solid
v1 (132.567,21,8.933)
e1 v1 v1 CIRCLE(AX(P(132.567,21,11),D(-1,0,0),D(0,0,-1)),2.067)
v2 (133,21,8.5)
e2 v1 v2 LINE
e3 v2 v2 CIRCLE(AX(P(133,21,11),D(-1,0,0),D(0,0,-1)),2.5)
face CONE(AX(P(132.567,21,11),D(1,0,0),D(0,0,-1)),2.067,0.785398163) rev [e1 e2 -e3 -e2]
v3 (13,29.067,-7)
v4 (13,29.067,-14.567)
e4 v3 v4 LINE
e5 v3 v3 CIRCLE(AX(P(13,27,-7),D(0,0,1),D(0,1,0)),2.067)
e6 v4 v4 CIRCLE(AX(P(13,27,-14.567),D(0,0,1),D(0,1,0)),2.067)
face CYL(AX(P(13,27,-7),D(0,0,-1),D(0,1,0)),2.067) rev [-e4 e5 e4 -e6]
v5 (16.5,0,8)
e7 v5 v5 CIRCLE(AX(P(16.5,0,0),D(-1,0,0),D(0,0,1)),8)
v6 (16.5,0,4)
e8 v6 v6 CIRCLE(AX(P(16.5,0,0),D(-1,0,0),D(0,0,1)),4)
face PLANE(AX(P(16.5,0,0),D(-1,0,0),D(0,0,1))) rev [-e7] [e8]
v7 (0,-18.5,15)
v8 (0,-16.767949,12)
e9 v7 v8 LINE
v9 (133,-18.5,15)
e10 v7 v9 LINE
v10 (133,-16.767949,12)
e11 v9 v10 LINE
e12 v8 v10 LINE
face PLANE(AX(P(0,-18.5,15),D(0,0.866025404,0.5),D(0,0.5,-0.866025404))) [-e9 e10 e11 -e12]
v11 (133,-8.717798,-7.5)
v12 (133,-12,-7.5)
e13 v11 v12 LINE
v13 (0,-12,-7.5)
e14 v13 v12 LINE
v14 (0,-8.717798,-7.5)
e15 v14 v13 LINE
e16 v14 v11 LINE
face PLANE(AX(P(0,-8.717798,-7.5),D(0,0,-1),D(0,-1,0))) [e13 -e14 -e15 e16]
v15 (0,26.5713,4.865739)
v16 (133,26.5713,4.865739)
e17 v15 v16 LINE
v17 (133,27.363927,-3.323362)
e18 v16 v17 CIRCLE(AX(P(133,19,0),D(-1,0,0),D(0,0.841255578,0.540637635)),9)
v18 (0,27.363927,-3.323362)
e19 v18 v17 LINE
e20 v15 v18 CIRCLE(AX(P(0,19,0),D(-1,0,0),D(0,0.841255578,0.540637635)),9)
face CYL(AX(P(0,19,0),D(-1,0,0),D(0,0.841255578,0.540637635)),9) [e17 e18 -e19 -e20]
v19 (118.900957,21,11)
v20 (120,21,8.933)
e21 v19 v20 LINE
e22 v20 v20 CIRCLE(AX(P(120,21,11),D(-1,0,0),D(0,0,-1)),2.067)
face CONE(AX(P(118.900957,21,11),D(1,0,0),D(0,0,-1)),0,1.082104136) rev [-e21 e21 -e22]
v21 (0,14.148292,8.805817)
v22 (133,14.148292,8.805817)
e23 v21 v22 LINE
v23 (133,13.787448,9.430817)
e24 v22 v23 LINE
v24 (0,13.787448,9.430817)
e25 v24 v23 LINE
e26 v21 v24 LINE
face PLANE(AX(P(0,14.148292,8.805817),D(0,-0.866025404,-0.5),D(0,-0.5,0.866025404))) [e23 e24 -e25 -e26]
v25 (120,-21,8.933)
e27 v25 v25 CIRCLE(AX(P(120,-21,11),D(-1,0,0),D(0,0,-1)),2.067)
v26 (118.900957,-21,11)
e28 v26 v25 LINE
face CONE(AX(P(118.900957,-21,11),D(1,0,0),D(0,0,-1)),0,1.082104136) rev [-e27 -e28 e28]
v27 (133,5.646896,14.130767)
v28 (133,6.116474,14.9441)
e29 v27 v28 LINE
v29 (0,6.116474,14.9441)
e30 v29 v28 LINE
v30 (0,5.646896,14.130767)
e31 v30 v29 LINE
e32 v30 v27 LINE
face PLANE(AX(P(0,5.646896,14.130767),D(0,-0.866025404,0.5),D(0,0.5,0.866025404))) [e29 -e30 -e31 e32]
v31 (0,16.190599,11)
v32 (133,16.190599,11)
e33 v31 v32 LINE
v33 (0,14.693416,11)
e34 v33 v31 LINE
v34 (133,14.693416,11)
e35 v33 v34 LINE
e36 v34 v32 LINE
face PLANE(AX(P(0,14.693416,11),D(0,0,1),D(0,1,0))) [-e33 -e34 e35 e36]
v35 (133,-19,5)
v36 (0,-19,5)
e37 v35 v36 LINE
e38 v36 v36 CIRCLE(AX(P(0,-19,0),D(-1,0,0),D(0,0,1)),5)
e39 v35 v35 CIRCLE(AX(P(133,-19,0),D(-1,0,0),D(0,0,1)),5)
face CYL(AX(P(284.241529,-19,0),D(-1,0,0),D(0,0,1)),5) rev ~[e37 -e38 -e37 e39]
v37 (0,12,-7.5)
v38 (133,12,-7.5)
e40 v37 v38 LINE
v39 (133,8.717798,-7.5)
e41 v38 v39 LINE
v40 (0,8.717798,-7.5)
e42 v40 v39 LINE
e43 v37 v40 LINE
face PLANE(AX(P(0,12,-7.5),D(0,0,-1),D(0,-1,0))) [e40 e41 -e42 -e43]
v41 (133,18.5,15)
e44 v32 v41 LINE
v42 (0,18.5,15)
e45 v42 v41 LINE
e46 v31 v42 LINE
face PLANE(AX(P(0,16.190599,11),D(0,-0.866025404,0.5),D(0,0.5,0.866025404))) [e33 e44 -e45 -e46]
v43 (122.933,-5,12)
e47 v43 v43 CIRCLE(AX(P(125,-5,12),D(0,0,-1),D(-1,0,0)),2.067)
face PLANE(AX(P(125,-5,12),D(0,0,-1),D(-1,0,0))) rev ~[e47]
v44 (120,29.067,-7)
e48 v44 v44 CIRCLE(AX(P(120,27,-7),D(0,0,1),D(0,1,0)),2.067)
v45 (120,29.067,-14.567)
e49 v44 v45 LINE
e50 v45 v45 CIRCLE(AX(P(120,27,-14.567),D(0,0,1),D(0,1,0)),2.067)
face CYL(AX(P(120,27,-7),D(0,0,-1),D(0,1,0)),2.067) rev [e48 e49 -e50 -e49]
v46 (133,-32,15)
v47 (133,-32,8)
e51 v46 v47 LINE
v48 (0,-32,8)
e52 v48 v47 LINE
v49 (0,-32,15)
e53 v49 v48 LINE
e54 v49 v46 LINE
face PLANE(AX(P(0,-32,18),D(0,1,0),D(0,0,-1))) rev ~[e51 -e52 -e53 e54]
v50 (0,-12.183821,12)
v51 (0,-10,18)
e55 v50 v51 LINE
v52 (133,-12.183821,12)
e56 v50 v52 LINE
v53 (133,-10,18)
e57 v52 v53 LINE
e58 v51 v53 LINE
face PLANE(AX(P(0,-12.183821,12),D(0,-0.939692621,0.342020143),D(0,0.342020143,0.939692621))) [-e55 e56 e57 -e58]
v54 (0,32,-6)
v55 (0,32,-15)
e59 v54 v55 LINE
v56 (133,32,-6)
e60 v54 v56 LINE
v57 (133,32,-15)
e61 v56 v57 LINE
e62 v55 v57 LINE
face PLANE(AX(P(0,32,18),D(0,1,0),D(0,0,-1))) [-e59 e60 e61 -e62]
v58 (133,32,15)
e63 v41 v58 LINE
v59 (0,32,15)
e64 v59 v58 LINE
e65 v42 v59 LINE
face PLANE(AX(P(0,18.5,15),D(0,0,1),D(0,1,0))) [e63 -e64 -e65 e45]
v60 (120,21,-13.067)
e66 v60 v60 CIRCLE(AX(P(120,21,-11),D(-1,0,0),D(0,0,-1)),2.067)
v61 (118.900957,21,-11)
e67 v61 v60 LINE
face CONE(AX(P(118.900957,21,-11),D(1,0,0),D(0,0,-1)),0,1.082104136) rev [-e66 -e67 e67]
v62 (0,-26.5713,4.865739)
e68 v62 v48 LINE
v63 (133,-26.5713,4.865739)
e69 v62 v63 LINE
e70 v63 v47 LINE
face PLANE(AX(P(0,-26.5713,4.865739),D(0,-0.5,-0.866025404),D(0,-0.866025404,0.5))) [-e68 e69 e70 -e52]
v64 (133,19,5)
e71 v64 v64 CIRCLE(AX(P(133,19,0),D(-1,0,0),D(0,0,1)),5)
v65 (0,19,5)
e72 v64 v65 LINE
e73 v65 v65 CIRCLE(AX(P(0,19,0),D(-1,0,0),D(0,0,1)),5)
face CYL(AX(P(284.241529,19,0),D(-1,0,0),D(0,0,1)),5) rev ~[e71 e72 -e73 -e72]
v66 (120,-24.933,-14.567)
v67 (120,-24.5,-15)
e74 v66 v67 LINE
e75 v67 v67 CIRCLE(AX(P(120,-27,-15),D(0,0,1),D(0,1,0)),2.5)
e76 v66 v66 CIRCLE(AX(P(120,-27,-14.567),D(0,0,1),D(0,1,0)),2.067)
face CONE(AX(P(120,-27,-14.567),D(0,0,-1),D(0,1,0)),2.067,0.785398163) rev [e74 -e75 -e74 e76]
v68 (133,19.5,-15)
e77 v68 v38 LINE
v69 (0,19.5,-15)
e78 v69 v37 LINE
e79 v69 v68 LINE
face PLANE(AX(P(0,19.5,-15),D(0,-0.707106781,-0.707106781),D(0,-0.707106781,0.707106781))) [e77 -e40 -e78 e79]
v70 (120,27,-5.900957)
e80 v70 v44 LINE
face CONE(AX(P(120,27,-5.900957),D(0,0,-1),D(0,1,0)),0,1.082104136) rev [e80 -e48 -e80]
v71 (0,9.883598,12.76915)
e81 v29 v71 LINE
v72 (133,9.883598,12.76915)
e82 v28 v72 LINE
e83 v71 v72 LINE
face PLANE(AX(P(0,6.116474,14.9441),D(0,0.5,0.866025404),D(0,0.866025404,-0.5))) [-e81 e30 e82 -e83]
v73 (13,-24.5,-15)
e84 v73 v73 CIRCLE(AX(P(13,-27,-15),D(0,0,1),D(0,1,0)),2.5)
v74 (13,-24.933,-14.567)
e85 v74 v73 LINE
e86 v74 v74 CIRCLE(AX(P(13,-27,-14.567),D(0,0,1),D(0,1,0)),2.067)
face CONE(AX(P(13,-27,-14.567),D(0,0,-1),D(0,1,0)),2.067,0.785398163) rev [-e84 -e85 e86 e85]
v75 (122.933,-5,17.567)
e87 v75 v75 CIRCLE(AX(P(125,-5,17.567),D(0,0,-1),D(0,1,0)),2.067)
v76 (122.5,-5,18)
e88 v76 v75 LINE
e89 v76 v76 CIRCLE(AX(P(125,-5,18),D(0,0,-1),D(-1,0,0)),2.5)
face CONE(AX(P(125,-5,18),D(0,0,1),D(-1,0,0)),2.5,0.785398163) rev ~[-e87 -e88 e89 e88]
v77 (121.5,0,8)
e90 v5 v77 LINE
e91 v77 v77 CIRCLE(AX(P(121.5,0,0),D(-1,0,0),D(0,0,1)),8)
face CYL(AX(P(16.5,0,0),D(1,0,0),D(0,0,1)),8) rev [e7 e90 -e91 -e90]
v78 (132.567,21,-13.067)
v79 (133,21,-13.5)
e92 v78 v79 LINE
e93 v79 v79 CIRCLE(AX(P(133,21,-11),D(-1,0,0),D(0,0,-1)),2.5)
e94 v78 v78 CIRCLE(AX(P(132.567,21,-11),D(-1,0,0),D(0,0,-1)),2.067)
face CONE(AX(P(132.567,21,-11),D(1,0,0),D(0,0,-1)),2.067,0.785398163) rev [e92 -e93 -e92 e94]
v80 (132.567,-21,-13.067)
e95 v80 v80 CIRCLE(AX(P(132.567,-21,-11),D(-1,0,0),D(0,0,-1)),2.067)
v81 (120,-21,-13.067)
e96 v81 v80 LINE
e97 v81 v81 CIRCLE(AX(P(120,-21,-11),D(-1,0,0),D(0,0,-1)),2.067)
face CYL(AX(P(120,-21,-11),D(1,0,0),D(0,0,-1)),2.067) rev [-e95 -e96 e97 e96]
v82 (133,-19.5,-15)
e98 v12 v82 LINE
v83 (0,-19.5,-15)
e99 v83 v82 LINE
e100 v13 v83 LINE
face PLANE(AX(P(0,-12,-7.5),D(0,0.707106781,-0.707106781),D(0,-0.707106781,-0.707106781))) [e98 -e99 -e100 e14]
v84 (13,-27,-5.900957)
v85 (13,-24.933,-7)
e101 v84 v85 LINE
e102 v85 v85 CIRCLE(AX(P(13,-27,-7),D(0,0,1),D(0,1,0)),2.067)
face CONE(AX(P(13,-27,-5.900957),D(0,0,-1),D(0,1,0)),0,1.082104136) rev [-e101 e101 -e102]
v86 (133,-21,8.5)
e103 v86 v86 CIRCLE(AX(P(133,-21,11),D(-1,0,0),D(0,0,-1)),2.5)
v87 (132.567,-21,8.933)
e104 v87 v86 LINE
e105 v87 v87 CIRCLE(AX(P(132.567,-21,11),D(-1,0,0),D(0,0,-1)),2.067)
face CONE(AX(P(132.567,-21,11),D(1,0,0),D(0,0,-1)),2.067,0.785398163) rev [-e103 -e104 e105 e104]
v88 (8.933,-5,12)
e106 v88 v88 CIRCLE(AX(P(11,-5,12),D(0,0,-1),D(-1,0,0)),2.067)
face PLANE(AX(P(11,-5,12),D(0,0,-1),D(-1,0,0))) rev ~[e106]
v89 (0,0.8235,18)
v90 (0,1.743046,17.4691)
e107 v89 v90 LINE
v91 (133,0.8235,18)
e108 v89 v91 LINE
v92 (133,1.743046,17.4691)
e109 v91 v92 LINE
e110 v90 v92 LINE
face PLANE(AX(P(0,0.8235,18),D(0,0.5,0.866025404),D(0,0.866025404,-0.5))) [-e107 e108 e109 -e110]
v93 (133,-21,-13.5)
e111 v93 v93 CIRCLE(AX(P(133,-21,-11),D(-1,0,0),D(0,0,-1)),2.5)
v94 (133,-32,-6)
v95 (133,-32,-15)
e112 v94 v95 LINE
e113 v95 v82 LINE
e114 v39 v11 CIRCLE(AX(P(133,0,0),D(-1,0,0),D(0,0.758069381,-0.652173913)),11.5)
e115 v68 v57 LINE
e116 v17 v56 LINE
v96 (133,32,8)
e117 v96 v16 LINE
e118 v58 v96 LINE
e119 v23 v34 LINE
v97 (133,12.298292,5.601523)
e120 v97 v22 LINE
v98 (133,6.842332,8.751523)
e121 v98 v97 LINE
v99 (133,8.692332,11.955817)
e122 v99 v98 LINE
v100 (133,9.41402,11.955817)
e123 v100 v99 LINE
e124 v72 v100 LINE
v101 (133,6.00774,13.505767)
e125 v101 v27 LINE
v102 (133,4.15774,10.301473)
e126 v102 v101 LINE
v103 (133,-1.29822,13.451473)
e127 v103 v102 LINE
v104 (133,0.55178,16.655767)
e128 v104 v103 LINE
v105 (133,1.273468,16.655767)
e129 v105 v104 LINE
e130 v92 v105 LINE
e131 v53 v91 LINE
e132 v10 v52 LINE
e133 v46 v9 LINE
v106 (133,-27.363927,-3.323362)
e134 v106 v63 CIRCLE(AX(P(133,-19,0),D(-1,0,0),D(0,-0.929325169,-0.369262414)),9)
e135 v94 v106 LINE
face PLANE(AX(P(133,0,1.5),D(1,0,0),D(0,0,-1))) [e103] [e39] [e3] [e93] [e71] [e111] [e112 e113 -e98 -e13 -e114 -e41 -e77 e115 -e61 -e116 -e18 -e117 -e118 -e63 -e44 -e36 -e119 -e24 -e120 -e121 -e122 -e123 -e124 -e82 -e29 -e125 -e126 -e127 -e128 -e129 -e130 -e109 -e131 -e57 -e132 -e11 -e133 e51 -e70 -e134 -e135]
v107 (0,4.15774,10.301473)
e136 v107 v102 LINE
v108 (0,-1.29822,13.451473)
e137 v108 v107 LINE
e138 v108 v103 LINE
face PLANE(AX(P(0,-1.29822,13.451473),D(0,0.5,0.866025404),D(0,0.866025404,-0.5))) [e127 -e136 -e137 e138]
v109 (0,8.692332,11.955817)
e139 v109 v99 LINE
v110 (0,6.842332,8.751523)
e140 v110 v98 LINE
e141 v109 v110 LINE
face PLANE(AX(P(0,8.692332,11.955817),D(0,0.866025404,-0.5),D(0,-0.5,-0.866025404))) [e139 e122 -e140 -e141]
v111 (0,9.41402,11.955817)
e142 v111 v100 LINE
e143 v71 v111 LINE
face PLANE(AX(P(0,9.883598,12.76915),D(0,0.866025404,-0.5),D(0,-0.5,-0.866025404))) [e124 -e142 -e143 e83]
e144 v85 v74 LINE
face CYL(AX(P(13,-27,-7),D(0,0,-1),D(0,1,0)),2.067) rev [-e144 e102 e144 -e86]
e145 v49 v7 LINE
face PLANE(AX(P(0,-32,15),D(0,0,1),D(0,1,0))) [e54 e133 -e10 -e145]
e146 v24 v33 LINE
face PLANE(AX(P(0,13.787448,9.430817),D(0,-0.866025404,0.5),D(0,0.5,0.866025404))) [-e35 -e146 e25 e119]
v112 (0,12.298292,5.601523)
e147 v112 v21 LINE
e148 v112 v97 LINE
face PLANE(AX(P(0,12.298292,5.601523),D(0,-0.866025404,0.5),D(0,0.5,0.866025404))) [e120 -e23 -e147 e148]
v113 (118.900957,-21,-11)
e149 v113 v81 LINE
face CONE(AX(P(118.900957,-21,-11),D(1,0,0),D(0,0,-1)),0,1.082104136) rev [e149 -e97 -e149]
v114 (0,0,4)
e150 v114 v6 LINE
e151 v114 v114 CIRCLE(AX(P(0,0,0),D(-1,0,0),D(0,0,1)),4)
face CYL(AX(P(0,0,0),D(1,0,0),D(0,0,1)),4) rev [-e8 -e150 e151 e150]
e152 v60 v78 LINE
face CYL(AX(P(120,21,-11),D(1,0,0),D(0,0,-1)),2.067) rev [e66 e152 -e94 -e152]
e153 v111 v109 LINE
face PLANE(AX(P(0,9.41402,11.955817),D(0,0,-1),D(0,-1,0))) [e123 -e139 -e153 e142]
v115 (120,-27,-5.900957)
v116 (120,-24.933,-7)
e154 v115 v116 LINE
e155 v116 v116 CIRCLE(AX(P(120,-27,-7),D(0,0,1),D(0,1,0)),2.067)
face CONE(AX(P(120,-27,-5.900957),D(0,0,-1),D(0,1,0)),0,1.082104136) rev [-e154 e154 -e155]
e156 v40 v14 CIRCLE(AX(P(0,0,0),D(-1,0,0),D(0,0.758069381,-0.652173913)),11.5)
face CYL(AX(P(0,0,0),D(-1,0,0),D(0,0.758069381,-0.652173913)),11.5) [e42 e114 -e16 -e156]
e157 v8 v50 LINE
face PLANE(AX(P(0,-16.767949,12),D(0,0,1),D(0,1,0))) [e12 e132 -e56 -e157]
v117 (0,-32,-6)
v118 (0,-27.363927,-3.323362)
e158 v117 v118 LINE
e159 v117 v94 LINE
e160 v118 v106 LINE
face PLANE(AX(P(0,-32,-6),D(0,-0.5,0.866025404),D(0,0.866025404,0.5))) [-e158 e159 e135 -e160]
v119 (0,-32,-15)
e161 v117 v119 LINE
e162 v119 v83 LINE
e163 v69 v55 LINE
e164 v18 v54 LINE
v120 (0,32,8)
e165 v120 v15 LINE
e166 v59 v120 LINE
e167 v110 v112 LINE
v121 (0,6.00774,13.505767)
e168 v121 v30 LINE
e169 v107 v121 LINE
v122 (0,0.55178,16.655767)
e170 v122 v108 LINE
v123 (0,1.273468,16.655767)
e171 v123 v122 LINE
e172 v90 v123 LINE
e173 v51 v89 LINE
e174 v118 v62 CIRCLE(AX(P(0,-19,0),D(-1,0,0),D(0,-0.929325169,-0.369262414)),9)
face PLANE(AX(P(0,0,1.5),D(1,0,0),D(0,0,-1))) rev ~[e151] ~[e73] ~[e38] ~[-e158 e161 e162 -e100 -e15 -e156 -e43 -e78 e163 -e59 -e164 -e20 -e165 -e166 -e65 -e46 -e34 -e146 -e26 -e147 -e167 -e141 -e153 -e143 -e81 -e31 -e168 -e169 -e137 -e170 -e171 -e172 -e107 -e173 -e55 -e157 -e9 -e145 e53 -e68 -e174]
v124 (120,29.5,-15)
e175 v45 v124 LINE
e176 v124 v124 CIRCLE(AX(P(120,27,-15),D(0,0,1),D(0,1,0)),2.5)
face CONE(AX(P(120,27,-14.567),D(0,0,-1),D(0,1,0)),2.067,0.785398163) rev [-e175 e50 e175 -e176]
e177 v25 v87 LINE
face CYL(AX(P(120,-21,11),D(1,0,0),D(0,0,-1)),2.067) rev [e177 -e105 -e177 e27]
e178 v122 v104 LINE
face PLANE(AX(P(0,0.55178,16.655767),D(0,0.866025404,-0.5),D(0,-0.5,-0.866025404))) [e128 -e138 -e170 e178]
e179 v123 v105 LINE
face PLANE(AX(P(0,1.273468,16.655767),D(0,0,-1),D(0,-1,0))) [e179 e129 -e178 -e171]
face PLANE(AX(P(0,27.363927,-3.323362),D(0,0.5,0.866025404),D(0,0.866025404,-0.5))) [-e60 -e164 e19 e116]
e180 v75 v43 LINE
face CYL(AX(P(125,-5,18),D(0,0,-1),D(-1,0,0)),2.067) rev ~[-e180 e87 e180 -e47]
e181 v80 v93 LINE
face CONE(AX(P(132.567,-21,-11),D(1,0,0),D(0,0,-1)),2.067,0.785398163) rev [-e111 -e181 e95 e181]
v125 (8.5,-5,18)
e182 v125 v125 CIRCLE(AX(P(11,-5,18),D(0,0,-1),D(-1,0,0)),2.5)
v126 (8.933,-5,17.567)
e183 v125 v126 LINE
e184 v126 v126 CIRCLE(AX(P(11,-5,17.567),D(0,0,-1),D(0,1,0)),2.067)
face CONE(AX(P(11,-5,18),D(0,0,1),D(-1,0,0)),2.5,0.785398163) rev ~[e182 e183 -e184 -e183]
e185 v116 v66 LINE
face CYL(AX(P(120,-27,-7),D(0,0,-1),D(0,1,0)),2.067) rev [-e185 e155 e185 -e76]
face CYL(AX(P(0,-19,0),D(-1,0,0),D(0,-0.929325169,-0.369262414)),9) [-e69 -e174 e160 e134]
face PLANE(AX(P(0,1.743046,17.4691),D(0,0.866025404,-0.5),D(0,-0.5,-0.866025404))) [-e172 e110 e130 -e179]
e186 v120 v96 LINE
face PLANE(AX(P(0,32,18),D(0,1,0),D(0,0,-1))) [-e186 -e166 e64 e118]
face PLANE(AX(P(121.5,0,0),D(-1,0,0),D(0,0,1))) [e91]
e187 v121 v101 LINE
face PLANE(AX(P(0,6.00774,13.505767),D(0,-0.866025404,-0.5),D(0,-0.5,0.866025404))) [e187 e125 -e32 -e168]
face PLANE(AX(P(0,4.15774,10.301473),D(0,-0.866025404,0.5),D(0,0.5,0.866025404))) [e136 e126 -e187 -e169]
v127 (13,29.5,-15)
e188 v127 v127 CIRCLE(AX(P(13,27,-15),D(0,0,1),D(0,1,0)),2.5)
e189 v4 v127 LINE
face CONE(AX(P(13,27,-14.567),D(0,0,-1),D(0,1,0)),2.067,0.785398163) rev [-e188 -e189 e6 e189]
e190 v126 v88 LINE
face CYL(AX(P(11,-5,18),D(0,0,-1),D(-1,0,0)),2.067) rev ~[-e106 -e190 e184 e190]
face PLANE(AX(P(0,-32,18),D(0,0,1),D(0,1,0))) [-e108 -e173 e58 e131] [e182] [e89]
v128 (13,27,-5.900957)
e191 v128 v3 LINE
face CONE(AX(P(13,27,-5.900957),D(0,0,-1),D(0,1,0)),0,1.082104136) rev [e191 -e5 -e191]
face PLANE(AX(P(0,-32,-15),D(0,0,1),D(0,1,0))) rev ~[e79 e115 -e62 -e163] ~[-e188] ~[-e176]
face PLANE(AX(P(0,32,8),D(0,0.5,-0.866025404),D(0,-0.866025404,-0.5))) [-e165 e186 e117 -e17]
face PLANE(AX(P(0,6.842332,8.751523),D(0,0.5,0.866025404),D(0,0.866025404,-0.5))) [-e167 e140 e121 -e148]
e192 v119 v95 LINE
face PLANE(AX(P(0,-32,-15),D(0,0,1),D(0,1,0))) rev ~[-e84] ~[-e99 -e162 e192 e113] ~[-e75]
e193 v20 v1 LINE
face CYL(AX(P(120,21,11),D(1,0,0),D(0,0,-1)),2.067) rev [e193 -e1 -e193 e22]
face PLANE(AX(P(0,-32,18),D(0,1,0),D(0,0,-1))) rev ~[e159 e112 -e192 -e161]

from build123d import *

# Parameters (mm, degrees)
SKETCH_1_W                  = 33
SKETCH_1_H                  = 64
EXTRUDE_1_DEPTH             = 133
HOLE_WIZARD_1_D             = 10
PATTERN_LINEAR_1_COUNT      = 2
PATTERN_LINEAR_1_PITCH      = 38
PATTERN_LINEAR_2_COUNT      = 2
PATTERN_LINEAR_2_PITCH      = 22
PATTERN_LINEAR_2_COUNT_DIR2 = 2
PATTERN_LINEAR_2_PITCH_DIR2 = 42
PATTERN_LINEAR_3_COUNT      = 2
PATTERN_LINEAR_3_PITCH      = 107
PATTERN_LINEAR_3_COUNT_DIR2 = 2
PATTERN_LINEAR_3_PITCH_DIR2 = 54
CUT_EXTRUDE_1_DEPTH         = 133
CUT_EXTRUDE_2_DEPTH         = 133
CUT_EXTRUDE_3_DEPTH         = 133
CUT_EXTRUDE_4_DEPTH         = 133
CUT_EXTRUDE_5_DEPTH         = 133
HOLE_WIZARD_4_D             = 4.134
HOLE_WIZARD_4_DEPTH         = 6
HOLE_WIZARD_4_CSINK_D       = 5
HOLE_WIZARD_4_CSINK_ANGLE   = 90
PATTERN_LINEAR_4_COUNT      = 2
PATTERN_LINEAR_4_PITCH      = 114


with BuildPart() as part:
    # 草图1 → 凸台-拉伸1 (new body)
    with BuildSketch(Plane(origin=(0, 0, 0), x_dir=(0, 0, -1), z_dir=(1, 0, 0))):
        with Locations((-1.5, 0)):
            Rectangle(SKETCH_1_W, SKETCH_1_H)
    extrude(amount=EXTRUDE_1_DEPTH)

    # 孔1 (through all)
    with Locations(Plane(origin=(133, 0, 0), x_dir=(0, 0, -1), z_dir=(1, 0, 0))):
        with Locations((0, 19)):
            hole_wizard_1 = Hole(HOLE_WIZARD_1_D / 2)

    # 阵列(线性)1: 孔1 ×2
    with Locations(*[(0, -i * PATTERN_LINEAR_1_PITCH, 0) for i in range(1, PATTERN_LINEAR_1_COUNT)]):
        add(hole_wizard_1, mode=Mode.SUBTRACT)

    # 草图5 → 孔2 (revolve, cut)
    with BuildSketch(Plane(origin=(133, 21, 11), x_dir=(0, 0, -1), z_dir=(0, 1, 0))):
        Polygon((0, 0), (0, 14.099043395), (2.067, 13), (2.067, 0.433), (2.5, 0), align=None)
    hole_wizard_2 = revolve(axis=Axis((147.308894879, 21, 11), (-1, 0, 0)), mode=Mode.SUBTRACT)

    # 阵列(线性)2: Hole Wizard 2 2 × 2
    with Locations(*[(0, -j * PATTERN_LINEAR_2_PITCH_DIR2, -i * PATTERN_LINEAR_2_PITCH) for i in range(PATTERN_LINEAR_2_COUNT) for j in range(PATTERN_LINEAR_2_COUNT_DIR2) if (i, j) != (0, 0)]):
        add(hole_wizard_2, mode=Mode.SUBTRACT)

    # 草图8 → 孔3 (revolve, cut)
    with BuildSketch(Plane(origin=(13, 27, -15), x_dir=(0, 1, 0), z_dir=(1, 0, 0))):
        Polygon((0, 0), (0, 9.099043395), (2.067, 8), (2.067, 0.433), (2.5, 0), align=None)
    hole_wizard_3 = revolve(axis=Axis((13, 27, -29.308894879), (0, 0, 1)), mode=Mode.SUBTRACT)

    # 阵列(线性)3: Hole Wizard 3 2 × 2
    with Locations(*[(i * PATTERN_LINEAR_3_PITCH, -j * PATTERN_LINEAR_3_PITCH_DIR2, 0) for i in range(PATTERN_LINEAR_3_COUNT) for j in range(PATTERN_LINEAR_3_COUNT_DIR2) if (i, j) != (0, 0)]):
        add(hole_wizard_3, mode=Mode.SUBTRACT)

    # 草图11 → 切除-旋转1 (revolve, cut)
    with BuildSketch(Plane.XY, mode=Mode.PRIVATE) as cut_revolve_1_sk:
        Polygon((0, 0), (0, 4), (16.5, 4), (16.5, 8), (121.5, 8), (121.5, 0), align=None)
    revolve(cut_revolve_1_sk.sketch.rotate(Axis((121.5, 0, 0), (-1, 0, 0)), 270), axis=Axis((121.5, 0, 0), (-1, 0, 0)), mode=Mode.SUBTRACT)

    # 草图12 → 切除-拉伸1 (cut)
    with BuildSketch(Plane(origin=(0, 0, 0), x_dir=(0, 0, -1), z_dir=(1, 0, 0))):
        with BuildLine():
            Line((-8, 32), (-4.865738712, 26.571300205))
            ThreePointArc((-4.865738712, 26.571300205), (-0.867061595, 27.958136201), (3.323361728, 27.36392652))
            Line((3.323361728, 27.36392652), (6, 32))
            Line((6, 32), (-8, 32))
        make_face()
    extrude(amount=CUT_EXTRUDE_1_DEPTH, mode=Mode.SUBTRACT)

    # 草图13 → 切除-拉伸2 (cut)
    with BuildSketch(Plane(origin=(0, 0, 0), x_dir=(0, 0, -1), z_dir=(1, 0, 0))):
        with BuildLine():
            Line((-8, -32), (6, -32))
            Line((6, -32), (3.323361728, -27.36392652))
            ThreePointArc((3.323361728, -27.36392652), (-0.867061595, -27.958136201), (-4.865738712, -26.571300205))
            Line((-4.865738712, -26.571300205), (-8, -32))
        make_face()
    extrude(amount=CUT_EXTRUDE_2_DEPTH, mode=Mode.SUBTRACT)

    # 草图14 → 切除-拉伸3 (cut)
    with BuildSketch(Plane(origin=(0, 0, 0), x_dir=(0, 0, -1), z_dir=(1, 0, 0))):
        with BuildLine():
            Line((7.5, -12), (15, -19.5))
            Line((15, -19.5), (15, 19.5))
            Line((15, 19.5), (7.5, 12))
            Line((7.5, 12), (7.5, 8.717797887))
            ThreePointArc((7.5, 8.717797887), (11.5, 0), (7.5, -8.717797887))
            Line((7.5, -8.717797887), (7.5, -12))
        make_face()
    extrude(amount=CUT_EXTRUDE_3_DEPTH, mode=Mode.SUBTRACT)

    # 草图15 → 切除-拉伸4 (cut)
    with BuildSketch(Plane(origin=(0, 0, 0), x_dir=(0, 0, -1), z_dir=(1, 0, 0))):
        Polygon((-18, -32), (-15, -32), (-15, -18.5), (-12, -16.767949192), (-12, -12.183821406), (-18, -10), align=None)
    extrude(amount=CUT_EXTRUDE_4_DEPTH, mode=Mode.SUBTRACT)

    # 草图16 → 切除-拉伸5 (cut)
    with BuildSketch(Plane(origin=(0, 0, 0), x_dir=(0, 0, -1), z_dir=(1, 0, 0))):
        Polygon((-18, 32), (-18, 0.8235), (-17.4691, 1.743045774), (-16.655766975, 1.273467733), (-16.655766975, 0.551779896), (-13.451472981, -1.298220104), (-10.301472981, 4.15773994), (-13.505766975, 6.00773994), (-14.130766975, 5.646896022), (-14.9441, 6.116474063), (-12.76915, 9.883597967), (-11.955816975, 9.414019926), (-11.955816975, 8.692332089), (-8.751522981, 6.842332089), (-5.601522981, 12.298292133), (-8.805816975, 14.148292133), (-9.430816975, 13.787448215), (-11, 14.693416457), (-11, 16.190598923), (-15, 18.5), (-15, 32), align=None)
    extrude(amount=CUT_EXTRUDE_5_DEPTH, mode=Mode.SUBTRACT)

    # 孔4
    with Locations(Plane.XY.offset(18)):
        with Locations((11, -5)):
            hole_wizard_4 = CounterSinkHole(HOLE_WIZARD_4_D / 2, HOLE_WIZARD_4_CSINK_D / 2, depth=HOLE_WIZARD_4_DEPTH, counter_sink_angle=HOLE_WIZARD_4_CSINK_ANGLE)

    # 阵列(线性)4: 孔4 ×2
    with Locations(*[(i * PATTERN_LINEAR_4_PITCH, 0, 0) for i in range(1, PATTERN_LINEAR_4_COUNT)]):
        add(hole_wizard_4, mode=Mode.SUBTRACT)


solid = part.part
